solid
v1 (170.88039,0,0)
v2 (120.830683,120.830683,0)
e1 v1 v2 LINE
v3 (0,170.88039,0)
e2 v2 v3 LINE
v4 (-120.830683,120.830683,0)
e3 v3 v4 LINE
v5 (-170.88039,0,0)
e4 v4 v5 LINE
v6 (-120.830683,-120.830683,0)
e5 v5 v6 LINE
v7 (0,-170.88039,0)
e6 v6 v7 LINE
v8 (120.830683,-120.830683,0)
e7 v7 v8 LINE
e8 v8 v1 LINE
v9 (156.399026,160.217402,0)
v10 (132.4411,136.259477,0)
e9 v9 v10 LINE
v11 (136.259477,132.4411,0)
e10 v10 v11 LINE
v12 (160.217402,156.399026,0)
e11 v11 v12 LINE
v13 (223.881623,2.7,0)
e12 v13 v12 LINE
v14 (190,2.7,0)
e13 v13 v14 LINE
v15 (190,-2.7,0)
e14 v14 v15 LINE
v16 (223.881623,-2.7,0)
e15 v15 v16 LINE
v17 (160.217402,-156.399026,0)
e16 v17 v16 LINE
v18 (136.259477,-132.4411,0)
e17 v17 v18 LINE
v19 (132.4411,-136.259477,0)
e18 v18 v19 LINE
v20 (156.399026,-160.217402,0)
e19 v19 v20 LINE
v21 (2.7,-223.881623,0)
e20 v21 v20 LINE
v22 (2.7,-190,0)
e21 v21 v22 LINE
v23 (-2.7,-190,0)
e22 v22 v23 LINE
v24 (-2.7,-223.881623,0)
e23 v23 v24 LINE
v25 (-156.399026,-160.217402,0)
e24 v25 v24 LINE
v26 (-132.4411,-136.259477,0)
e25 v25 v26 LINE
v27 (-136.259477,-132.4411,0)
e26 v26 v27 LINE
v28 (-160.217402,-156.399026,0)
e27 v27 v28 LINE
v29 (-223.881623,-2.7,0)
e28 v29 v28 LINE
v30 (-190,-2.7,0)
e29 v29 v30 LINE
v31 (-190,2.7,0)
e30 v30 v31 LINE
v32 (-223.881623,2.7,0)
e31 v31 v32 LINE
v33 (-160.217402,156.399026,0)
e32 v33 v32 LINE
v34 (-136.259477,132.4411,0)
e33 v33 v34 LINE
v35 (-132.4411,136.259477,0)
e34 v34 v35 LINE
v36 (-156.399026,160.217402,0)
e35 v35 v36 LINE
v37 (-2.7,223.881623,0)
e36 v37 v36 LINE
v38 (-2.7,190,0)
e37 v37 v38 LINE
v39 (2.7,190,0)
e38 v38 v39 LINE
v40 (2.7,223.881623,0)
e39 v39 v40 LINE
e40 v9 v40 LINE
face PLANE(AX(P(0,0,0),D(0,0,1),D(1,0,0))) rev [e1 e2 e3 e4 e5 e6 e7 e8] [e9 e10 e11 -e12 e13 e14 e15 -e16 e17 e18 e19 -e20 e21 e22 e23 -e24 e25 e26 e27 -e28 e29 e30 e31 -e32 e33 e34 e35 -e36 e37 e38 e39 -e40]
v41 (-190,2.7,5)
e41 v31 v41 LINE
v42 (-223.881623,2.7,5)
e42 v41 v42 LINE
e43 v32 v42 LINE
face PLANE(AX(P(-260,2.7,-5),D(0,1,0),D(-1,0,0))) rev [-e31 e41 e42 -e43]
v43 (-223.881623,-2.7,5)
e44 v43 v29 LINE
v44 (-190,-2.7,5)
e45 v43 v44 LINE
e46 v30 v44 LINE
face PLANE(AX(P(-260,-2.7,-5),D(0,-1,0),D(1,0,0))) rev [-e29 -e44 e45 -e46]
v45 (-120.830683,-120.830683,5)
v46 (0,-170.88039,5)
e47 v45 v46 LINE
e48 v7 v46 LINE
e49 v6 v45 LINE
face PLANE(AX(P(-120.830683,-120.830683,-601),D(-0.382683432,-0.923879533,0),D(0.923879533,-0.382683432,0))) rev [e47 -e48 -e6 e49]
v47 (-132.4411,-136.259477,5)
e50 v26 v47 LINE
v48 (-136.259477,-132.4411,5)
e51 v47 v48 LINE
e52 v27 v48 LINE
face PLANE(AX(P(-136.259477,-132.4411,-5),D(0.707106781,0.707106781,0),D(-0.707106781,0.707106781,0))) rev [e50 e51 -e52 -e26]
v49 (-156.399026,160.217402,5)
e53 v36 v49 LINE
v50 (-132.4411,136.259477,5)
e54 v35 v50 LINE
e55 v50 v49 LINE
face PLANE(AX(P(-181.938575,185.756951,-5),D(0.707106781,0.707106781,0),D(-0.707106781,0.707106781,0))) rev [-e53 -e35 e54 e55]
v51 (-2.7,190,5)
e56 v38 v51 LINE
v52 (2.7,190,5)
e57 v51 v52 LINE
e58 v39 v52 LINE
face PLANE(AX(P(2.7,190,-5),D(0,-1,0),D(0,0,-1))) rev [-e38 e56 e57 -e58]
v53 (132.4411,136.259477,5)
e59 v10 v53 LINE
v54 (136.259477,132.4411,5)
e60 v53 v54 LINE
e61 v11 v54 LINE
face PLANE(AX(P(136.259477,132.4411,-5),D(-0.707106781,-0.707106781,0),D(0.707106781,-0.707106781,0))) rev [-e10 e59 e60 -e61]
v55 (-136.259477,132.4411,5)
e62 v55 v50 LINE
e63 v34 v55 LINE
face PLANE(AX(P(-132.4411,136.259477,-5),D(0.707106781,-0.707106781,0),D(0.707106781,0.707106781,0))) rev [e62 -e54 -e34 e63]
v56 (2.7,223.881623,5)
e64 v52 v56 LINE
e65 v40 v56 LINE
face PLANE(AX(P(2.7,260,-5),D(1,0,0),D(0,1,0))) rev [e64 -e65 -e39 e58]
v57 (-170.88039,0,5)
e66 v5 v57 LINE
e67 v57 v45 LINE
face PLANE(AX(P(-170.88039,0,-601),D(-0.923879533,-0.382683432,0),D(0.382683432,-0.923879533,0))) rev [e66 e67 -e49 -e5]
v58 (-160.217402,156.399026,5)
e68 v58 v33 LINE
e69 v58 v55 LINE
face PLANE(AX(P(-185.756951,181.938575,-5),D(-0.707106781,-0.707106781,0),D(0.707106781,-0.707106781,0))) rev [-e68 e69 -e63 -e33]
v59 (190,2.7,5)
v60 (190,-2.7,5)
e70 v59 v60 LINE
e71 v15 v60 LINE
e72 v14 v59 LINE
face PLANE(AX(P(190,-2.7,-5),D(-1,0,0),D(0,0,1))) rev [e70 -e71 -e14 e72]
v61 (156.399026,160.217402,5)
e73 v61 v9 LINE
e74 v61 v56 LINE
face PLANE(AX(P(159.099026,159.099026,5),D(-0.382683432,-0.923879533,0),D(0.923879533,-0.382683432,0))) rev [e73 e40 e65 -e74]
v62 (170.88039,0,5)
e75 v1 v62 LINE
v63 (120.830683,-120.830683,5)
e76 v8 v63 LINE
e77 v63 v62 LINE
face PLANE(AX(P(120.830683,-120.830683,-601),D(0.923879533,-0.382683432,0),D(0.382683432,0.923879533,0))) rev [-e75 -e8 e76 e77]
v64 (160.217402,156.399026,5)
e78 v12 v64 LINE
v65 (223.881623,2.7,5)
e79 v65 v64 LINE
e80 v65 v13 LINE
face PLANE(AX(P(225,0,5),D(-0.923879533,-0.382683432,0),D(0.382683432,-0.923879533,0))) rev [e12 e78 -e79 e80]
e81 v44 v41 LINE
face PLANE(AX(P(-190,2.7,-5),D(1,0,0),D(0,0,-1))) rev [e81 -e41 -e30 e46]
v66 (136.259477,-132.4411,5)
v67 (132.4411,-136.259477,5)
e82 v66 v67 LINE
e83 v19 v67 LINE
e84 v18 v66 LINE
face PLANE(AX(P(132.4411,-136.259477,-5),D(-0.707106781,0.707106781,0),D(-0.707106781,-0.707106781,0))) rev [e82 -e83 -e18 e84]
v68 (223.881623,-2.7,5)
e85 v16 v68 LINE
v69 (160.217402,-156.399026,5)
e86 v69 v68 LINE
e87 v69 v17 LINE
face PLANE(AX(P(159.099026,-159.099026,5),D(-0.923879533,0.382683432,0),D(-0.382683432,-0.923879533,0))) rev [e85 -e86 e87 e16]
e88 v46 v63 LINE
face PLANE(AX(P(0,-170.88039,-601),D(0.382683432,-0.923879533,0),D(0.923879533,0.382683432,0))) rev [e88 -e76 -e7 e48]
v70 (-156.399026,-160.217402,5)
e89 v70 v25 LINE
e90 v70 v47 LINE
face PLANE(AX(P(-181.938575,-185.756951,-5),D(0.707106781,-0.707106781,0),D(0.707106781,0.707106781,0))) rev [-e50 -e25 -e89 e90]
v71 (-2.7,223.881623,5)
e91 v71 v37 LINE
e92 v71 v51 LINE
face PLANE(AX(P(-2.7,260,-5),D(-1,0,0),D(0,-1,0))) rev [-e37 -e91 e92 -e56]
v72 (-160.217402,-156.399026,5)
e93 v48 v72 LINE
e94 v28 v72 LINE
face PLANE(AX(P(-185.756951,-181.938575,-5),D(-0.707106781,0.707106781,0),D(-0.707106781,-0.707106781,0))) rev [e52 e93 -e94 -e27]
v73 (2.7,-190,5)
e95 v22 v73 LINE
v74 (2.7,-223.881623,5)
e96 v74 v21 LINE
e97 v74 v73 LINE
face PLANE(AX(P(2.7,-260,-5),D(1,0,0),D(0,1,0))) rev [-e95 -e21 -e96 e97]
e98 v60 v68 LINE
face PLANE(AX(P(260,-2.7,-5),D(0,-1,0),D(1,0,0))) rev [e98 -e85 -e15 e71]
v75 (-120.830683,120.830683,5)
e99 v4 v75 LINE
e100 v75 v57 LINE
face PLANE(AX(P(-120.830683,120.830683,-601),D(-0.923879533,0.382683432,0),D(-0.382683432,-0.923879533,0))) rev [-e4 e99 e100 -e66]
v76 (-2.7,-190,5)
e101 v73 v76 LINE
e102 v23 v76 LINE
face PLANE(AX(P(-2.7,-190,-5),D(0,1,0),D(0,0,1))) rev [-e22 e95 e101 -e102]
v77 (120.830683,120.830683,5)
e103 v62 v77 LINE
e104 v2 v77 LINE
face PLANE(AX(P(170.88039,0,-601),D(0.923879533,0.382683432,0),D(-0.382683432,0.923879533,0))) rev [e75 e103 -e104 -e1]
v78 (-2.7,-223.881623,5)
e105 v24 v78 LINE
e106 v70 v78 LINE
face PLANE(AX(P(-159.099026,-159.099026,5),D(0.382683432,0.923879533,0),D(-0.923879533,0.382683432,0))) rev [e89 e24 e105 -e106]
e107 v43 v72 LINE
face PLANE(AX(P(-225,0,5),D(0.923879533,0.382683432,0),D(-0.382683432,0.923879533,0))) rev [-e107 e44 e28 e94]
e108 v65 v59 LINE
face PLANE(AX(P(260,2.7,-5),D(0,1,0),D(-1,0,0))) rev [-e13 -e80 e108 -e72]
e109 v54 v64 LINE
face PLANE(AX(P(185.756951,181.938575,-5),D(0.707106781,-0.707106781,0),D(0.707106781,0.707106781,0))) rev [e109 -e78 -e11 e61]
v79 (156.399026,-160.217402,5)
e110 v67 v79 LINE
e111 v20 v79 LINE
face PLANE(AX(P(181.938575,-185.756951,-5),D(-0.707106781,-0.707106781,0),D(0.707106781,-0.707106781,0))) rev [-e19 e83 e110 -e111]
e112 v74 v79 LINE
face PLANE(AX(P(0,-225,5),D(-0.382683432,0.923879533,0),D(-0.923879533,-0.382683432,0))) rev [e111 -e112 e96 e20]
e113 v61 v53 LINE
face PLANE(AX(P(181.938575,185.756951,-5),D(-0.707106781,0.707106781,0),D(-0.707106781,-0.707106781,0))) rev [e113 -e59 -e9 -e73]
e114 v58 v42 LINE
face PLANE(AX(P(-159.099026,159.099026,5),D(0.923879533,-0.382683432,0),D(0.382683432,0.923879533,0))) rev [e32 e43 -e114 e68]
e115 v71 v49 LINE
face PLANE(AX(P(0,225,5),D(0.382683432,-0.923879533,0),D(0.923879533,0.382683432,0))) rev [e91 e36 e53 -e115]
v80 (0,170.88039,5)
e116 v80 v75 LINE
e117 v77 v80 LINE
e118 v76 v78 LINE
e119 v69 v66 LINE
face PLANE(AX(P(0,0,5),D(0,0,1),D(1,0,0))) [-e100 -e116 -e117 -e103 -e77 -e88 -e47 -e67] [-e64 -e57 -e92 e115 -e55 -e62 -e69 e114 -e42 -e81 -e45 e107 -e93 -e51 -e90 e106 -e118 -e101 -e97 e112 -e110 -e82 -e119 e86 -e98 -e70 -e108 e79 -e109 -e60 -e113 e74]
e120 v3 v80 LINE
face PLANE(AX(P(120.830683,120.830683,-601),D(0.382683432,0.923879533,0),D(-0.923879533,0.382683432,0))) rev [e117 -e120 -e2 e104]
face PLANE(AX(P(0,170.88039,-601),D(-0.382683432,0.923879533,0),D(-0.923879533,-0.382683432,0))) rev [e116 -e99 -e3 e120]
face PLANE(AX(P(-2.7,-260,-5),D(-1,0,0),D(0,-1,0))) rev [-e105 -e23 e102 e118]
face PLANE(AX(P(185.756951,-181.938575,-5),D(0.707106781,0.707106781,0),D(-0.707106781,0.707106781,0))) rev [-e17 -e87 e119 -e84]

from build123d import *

# Parameters (mm, degrees)
EXTRUDE_1_DEPTH     = 5
CUT_EXTRUDE_1_DEPTH = 606
SKETCH_4_W          = 70
SKETCH_4_H          = 5.4
SKETCH_4_W_2        = 5.4
SKETCH_4_H_2        = 70
CUT_EXTRUDE_2_DEPTH = 10


with BuildPart() as part:
    # 草图1 → 凸台-拉伸1 (new body)
    with BuildSketch(Plane.XY):
        Polygon((159.099025767, 159.099025767), (0, 225), (-159.099025767, 159.099025767), (-225, 0), (-159.099025767, -159.099025767), (0, -225), (159.099025767, -159.099025767), (225, 0), align=None)
    extrude(amount=EXTRUDE_1_DEPTH)

    # 草图2 → 切除-拉伸1 (cut)
    with BuildSketch(Plane.XY.offset(5)):
        Polygon((0, 170.880389985), (-120.83068253, 120.83068253), (-170.880389985, 0), (-120.83068253, -120.83068253), (0, -170.880389985), (120.83068253, -120.83068253), (170.880389985, 0), (120.83068253, 120.83068253), align=None)
    extrude(amount=-CUT_EXTRUDE_1_DEPTH, mode=Mode.SUBTRACT)

    # 草图4 → 切除-拉伸2 (cut)
    with BuildSketch(Plane.XY.offset(5)):
        Polygon((185.756951418, -181.938574799), (136.259476735, -132.441100116), (132.441100116, -136.259476735), (181.938574799, -185.756951418), align=None)
        with Locations((225, 0)):
            Rectangle(SKETCH_4_W, SKETCH_4_H)
        with Locations((0, -225)):
            Rectangle(SKETCH_4_W_2, SKETCH_4_H_2)
        Polygon((-181.938574799, -185.756951418), (-132.441100116, -136.259476735), (-136.259476735, -132.441100116), (-185.756951418, -181.938574799), align=None)
        with Locations((-225, 0)):
            Rectangle(SKETCH_4_W, SKETCH_4_H)
        Polygon((-185.756951418, 181.938574799), (-136.259476735, 132.441100116), (-132.441100116, 136.259476735), (-181.938574799, 185.756951418), align=None)
        with Locations((0, 225)):
            Rectangle(SKETCH_4_W_2, SKETCH_4_H_2)
        Polygon((181.938574799, 185.756951418), (132.441100116, 136.259476735), (136.259476735, 132.441100116), (185.756951418, 181.938574799), align=None)
    extrude(amount=-CUT_EXTRUDE_2_DEPTH, mode=Mode.SUBTRACT)


solid = part.part
